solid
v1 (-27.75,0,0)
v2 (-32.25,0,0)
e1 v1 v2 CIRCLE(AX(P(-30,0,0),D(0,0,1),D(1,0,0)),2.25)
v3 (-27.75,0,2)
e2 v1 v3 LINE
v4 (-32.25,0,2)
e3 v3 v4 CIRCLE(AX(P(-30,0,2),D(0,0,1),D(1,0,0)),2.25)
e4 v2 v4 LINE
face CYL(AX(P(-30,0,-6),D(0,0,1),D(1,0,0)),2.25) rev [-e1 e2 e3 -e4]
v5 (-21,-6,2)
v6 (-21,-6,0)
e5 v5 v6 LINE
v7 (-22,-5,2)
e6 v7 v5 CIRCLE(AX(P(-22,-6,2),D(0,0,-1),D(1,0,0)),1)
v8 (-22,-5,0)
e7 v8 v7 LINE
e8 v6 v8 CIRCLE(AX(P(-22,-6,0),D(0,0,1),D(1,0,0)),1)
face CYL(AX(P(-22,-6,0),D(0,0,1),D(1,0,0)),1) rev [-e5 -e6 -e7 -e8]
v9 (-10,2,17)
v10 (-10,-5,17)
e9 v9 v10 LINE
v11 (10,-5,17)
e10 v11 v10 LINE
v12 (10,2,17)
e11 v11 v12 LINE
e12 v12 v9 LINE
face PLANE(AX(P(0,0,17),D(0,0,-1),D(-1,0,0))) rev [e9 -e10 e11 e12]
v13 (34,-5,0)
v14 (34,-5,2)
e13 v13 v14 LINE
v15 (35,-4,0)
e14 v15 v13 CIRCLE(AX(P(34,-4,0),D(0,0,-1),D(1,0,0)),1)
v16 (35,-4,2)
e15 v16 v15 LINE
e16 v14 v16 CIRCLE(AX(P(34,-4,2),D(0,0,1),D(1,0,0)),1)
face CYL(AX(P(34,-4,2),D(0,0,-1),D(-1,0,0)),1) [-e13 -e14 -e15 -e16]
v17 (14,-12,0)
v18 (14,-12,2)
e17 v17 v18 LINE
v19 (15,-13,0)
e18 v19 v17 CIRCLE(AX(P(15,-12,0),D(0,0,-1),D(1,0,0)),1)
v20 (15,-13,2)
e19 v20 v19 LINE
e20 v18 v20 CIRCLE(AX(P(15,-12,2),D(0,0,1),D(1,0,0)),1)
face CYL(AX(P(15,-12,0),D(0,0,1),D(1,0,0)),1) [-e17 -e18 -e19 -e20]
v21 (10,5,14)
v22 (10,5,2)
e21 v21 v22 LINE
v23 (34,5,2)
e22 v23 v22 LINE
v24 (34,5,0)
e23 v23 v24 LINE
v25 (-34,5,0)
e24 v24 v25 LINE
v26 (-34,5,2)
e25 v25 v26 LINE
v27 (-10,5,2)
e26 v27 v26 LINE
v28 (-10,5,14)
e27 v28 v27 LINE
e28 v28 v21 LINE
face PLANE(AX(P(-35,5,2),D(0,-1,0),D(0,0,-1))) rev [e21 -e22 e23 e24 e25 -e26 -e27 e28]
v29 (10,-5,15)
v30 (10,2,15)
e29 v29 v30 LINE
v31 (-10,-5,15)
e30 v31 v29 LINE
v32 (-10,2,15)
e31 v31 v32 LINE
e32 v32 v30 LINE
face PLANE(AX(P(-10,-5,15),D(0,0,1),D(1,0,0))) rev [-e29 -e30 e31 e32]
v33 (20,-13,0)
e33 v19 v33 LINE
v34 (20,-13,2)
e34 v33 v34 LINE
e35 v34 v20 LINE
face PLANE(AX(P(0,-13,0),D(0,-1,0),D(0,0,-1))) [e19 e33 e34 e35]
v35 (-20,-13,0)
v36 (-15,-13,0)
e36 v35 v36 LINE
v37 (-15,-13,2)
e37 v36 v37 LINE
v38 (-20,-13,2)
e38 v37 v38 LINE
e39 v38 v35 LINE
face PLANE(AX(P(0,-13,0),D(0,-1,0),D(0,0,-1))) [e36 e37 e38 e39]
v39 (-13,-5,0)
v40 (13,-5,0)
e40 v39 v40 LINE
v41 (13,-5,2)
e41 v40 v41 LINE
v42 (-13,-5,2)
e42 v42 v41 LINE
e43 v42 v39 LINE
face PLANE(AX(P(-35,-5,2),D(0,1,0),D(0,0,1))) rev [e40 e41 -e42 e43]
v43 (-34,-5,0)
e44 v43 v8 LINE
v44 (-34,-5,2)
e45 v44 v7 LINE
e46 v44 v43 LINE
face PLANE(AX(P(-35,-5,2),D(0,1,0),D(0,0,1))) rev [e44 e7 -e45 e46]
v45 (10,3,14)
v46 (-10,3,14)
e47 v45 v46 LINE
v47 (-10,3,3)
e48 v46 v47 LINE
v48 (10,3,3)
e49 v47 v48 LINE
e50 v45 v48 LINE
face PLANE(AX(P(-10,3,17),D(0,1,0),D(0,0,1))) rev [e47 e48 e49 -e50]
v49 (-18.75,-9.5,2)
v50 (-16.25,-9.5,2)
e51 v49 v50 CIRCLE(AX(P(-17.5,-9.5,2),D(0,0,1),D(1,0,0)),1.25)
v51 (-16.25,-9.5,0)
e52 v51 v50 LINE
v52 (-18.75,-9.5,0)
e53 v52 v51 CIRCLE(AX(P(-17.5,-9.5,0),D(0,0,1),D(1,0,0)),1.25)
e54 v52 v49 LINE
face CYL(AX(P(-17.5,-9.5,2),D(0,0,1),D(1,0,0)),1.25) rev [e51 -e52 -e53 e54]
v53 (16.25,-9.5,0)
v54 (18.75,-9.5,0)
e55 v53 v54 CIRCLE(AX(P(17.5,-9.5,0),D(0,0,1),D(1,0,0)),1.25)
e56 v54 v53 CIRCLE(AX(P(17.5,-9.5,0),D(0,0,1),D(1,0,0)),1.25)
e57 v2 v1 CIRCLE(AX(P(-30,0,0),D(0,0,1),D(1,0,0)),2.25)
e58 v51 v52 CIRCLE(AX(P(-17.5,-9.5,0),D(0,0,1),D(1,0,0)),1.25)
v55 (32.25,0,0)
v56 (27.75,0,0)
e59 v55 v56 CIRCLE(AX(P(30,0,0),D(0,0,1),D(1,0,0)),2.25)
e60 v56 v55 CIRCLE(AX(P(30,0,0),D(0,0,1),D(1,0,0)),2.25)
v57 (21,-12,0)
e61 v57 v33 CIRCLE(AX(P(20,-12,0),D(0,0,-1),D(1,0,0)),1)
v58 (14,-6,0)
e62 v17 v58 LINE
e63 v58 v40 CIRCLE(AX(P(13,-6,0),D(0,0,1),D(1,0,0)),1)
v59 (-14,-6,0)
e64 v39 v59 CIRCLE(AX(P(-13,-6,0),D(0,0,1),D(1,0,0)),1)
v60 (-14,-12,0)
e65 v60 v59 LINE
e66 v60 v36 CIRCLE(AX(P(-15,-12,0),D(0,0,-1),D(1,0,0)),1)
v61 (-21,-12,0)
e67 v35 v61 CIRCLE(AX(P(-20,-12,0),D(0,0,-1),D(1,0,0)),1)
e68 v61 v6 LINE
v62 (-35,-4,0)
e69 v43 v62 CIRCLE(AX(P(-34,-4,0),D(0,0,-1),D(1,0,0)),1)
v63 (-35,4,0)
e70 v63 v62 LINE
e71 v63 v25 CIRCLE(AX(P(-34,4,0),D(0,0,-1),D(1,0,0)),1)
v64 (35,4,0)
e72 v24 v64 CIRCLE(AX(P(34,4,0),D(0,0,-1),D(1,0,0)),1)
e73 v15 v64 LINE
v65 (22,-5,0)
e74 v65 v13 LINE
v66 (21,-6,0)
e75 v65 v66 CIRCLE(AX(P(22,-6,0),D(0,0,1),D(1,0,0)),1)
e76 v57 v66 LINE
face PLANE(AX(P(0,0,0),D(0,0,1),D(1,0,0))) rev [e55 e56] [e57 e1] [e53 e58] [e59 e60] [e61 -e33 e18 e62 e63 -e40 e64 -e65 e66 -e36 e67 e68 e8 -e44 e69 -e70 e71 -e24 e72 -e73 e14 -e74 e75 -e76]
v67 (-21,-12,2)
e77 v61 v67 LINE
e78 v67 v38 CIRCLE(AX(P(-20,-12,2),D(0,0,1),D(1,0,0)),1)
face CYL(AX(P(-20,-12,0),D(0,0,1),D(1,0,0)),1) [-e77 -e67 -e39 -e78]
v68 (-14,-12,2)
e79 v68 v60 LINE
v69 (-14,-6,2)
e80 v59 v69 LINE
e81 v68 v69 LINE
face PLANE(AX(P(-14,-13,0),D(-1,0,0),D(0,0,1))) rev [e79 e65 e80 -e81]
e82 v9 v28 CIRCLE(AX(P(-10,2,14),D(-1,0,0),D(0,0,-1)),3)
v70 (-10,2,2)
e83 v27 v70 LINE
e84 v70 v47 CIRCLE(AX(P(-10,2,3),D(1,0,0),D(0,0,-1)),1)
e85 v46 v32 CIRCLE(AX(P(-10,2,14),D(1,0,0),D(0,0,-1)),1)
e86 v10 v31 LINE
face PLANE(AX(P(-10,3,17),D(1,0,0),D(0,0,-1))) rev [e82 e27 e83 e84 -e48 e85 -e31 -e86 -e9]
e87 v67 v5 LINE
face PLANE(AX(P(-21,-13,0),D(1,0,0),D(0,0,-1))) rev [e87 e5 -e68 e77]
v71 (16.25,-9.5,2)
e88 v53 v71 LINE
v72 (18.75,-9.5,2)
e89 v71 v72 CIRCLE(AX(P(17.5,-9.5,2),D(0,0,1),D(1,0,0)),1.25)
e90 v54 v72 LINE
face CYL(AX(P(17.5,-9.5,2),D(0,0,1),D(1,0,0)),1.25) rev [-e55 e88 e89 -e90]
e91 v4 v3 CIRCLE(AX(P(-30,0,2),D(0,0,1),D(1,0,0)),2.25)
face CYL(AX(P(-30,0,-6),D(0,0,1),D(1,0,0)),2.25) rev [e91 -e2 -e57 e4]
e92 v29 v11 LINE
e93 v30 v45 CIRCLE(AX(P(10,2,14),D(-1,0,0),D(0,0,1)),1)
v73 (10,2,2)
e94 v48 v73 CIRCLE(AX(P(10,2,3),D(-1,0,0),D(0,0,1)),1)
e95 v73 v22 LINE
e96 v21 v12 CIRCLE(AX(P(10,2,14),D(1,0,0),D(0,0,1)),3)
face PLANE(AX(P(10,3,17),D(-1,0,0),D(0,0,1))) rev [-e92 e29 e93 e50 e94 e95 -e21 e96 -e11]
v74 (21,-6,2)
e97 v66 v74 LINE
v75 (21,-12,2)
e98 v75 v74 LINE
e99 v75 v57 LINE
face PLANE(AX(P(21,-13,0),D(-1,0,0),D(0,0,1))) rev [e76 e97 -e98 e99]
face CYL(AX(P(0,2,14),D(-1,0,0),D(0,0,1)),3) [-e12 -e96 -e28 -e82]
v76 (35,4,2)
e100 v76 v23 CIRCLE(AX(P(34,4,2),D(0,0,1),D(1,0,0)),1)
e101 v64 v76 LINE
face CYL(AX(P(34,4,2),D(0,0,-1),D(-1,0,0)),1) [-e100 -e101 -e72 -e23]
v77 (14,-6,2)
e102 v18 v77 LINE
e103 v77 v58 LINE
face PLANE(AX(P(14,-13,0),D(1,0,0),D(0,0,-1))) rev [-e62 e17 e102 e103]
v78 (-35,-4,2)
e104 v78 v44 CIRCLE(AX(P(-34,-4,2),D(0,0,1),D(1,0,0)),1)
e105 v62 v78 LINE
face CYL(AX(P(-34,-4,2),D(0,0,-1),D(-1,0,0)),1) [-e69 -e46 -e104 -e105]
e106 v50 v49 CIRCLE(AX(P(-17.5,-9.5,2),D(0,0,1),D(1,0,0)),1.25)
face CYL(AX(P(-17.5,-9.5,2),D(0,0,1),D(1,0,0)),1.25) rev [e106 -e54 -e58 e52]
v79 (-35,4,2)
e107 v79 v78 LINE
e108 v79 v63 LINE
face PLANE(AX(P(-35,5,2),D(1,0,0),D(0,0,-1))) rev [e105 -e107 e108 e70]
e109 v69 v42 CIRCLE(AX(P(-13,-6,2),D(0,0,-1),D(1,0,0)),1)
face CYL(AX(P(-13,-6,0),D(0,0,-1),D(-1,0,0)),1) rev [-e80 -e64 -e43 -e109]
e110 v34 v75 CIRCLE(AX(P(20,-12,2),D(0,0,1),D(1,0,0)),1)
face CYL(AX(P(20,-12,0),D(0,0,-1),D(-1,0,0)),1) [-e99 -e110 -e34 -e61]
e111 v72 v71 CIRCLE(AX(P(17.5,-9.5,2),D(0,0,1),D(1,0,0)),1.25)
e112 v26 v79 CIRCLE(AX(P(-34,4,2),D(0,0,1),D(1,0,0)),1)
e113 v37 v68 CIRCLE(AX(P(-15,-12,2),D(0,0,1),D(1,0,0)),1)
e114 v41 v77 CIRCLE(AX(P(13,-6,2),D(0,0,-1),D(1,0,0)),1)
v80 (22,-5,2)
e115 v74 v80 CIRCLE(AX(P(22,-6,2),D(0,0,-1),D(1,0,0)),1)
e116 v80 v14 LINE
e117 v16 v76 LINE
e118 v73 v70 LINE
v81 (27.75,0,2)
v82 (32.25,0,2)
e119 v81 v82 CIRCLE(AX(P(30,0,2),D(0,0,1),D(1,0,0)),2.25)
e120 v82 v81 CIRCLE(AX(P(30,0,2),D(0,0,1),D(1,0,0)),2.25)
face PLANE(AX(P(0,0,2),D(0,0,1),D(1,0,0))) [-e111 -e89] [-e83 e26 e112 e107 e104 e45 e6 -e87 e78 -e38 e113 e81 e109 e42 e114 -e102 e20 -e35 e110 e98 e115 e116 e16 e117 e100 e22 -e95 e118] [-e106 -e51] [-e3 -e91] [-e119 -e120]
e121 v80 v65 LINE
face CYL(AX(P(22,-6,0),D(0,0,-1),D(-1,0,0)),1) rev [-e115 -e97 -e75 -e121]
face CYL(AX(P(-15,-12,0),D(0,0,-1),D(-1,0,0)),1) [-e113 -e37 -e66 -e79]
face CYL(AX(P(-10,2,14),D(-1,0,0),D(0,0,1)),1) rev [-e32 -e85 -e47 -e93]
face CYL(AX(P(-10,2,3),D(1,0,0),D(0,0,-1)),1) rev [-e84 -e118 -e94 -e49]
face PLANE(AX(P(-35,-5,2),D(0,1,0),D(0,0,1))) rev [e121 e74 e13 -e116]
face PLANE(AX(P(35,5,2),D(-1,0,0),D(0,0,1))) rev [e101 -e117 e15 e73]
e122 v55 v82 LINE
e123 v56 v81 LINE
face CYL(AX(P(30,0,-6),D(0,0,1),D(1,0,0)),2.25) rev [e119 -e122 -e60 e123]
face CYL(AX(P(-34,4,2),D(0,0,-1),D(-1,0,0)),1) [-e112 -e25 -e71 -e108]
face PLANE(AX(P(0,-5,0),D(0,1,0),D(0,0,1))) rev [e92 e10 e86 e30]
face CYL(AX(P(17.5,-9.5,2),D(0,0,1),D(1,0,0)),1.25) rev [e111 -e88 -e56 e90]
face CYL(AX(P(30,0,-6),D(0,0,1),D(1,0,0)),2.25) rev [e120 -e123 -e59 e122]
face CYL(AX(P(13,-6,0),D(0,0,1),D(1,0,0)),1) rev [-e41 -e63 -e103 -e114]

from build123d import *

# Parameters (mm, degrees)
SKETCH1_W             = 70
SKETCH1_H             = 10
BOSS_EXTRUDE1_DEPTH   = 2
SKETCH2_W             = 20
SKETCH2_H             = 2
BOSS_EXTRUDE2_DEPTH   = 15
SKETCH3_W             = 20
SKETCH3_H             = 2
BOSS_EXTRUDE3_DEPTH   = 8
FILLET2_R             = 1
FILLET3_R             = 3
SKETCH4_R             = 2.25
CUT_EXTRUDE1_DEPTH    = 8
SKETCH6_W             = 7
SKETCH6_H             = 2
BOSS_EXTRUDE4_DEPTH   = 8
FILLET4_R             = 1
M3_TAPPED_HOLE1_D     = 2.5
M3_TAPPED_HOLE1_DEPTH = 7.5
M3_TAPPED_HOLE1_TIP   = 0.751075774
FILLET5_R             = 1


with BuildPart() as part:
    # Sketch1 → Boss-Extrude1 (new body)
    with BuildSketch(Plane.XY):
        Rectangle(SKETCH1_W, SKETCH1_H)
    extrude(amount=BOSS_EXTRUDE1_DEPTH)

    # Sketch2 → Boss-Extrude2 (add)
    with BuildSketch(Plane.XY.offset(2)):
        with Locations((0, 4)):
            Rectangle(SKETCH2_W, SKETCH2_H)
    extrude(amount=BOSS_EXTRUDE2_DEPTH)

    # Sketch3 → Boss-Extrude3 (add)
    with BuildSketch(Plane(origin=(0, 3, 0), x_dir=(-1, 0, 0), z_dir=(0, -1, 0))):
        with Locations((0, -16)):
            Rectangle(SKETCH3_W, SKETCH3_H)
    extrude(amount=BOSS_EXTRUDE3_DEPTH)

    # Fillet2
    fillet2_edges = [part.edges().sort_by_distance(p)[0] for p in [
        (0, 3, 2),
        (0, 3, 15),
    ]]
    fillet(fillet2_edges, radius=FILLET2_R)

    # Fillet3
    fillet3_edges = [part.edges().sort_by_distance(p)[0] for p in [
        (0, 5, 17),
    ]]
    fillet(fillet3_edges, radius=FILLET3_R)

    # Sketch4 → Cut-Extrude1 (cut)
    with BuildSketch(Plane.XY.offset(2)):
        with Locations((-30, 0)):
            Circle(SKETCH4_R)
        with Locations((30, 0)):
            Circle(SKETCH4_R)
    extrude(amount=-CUT_EXTRUDE1_DEPTH, mode=Mode.SUBTRACT)

    # Sketch6 → Boss-Extrude4 (add)
    with BuildSketch(Plane(origin=(0, -5, 0), x_dir=(-1, 0, 0), z_dir=(0, -1, 0))):
        with Locations((-17.5, -1)):
            Rectangle(SKETCH6_W, SKETCH6_H)
        with Locations((17.5, -1)):
            Rectangle(SKETCH6_W, SKETCH6_H)
    extrude(amount=BOSS_EXTRUDE4_DEPTH)

    # Fillet4
    fillet4_edges = [part.edges().sort_by_distance(p)[0] for p in [
        (35, -5, 1),
        (-35, -5, 1),
        (-35, 5, 1),
        (35, 5, 1),
    ]]
    fillet(fillet4_edges, radius=FILLET4_R)

    # M3 Tapped Hole1
    with Locations(Plane(origin=(-17.5, -9.5, 2), x_dir=(1, 0, 0), z_dir=(0, 0, 1))):
        with Locations((0, 0), (35, 0)):
            Hole(M3_TAPPED_HOLE1_D / 2, depth=M3_TAPPED_HOLE1_DEPTH)
            with Locations((0, 0, -(M3_TAPPED_HOLE1_DEPTH + M3_TAPPED_HOLE1_TIP / 2))):  # 118° drill point
                Cone(0, M3_TAPPED_HOLE1_D / 2, M3_TAPPED_HOLE1_TIP, mode=Mode.SUBTRACT)

    # Fillet5
    fillet5_edges = [part.edges().sort_by_distance(p)[0] for p in [
        (14, -5, 1),
        (21, -5, 1),
        (14, -13, 1),
        (21, -13, 1),
        (-21, -5, 1),
        (-14, -5, 1),
        (-21, -13, 1),
        (-14, -13, 1),
    ]]
    fillet(fillet5_edges, radius=FILLET5_R)


solid = part.part
